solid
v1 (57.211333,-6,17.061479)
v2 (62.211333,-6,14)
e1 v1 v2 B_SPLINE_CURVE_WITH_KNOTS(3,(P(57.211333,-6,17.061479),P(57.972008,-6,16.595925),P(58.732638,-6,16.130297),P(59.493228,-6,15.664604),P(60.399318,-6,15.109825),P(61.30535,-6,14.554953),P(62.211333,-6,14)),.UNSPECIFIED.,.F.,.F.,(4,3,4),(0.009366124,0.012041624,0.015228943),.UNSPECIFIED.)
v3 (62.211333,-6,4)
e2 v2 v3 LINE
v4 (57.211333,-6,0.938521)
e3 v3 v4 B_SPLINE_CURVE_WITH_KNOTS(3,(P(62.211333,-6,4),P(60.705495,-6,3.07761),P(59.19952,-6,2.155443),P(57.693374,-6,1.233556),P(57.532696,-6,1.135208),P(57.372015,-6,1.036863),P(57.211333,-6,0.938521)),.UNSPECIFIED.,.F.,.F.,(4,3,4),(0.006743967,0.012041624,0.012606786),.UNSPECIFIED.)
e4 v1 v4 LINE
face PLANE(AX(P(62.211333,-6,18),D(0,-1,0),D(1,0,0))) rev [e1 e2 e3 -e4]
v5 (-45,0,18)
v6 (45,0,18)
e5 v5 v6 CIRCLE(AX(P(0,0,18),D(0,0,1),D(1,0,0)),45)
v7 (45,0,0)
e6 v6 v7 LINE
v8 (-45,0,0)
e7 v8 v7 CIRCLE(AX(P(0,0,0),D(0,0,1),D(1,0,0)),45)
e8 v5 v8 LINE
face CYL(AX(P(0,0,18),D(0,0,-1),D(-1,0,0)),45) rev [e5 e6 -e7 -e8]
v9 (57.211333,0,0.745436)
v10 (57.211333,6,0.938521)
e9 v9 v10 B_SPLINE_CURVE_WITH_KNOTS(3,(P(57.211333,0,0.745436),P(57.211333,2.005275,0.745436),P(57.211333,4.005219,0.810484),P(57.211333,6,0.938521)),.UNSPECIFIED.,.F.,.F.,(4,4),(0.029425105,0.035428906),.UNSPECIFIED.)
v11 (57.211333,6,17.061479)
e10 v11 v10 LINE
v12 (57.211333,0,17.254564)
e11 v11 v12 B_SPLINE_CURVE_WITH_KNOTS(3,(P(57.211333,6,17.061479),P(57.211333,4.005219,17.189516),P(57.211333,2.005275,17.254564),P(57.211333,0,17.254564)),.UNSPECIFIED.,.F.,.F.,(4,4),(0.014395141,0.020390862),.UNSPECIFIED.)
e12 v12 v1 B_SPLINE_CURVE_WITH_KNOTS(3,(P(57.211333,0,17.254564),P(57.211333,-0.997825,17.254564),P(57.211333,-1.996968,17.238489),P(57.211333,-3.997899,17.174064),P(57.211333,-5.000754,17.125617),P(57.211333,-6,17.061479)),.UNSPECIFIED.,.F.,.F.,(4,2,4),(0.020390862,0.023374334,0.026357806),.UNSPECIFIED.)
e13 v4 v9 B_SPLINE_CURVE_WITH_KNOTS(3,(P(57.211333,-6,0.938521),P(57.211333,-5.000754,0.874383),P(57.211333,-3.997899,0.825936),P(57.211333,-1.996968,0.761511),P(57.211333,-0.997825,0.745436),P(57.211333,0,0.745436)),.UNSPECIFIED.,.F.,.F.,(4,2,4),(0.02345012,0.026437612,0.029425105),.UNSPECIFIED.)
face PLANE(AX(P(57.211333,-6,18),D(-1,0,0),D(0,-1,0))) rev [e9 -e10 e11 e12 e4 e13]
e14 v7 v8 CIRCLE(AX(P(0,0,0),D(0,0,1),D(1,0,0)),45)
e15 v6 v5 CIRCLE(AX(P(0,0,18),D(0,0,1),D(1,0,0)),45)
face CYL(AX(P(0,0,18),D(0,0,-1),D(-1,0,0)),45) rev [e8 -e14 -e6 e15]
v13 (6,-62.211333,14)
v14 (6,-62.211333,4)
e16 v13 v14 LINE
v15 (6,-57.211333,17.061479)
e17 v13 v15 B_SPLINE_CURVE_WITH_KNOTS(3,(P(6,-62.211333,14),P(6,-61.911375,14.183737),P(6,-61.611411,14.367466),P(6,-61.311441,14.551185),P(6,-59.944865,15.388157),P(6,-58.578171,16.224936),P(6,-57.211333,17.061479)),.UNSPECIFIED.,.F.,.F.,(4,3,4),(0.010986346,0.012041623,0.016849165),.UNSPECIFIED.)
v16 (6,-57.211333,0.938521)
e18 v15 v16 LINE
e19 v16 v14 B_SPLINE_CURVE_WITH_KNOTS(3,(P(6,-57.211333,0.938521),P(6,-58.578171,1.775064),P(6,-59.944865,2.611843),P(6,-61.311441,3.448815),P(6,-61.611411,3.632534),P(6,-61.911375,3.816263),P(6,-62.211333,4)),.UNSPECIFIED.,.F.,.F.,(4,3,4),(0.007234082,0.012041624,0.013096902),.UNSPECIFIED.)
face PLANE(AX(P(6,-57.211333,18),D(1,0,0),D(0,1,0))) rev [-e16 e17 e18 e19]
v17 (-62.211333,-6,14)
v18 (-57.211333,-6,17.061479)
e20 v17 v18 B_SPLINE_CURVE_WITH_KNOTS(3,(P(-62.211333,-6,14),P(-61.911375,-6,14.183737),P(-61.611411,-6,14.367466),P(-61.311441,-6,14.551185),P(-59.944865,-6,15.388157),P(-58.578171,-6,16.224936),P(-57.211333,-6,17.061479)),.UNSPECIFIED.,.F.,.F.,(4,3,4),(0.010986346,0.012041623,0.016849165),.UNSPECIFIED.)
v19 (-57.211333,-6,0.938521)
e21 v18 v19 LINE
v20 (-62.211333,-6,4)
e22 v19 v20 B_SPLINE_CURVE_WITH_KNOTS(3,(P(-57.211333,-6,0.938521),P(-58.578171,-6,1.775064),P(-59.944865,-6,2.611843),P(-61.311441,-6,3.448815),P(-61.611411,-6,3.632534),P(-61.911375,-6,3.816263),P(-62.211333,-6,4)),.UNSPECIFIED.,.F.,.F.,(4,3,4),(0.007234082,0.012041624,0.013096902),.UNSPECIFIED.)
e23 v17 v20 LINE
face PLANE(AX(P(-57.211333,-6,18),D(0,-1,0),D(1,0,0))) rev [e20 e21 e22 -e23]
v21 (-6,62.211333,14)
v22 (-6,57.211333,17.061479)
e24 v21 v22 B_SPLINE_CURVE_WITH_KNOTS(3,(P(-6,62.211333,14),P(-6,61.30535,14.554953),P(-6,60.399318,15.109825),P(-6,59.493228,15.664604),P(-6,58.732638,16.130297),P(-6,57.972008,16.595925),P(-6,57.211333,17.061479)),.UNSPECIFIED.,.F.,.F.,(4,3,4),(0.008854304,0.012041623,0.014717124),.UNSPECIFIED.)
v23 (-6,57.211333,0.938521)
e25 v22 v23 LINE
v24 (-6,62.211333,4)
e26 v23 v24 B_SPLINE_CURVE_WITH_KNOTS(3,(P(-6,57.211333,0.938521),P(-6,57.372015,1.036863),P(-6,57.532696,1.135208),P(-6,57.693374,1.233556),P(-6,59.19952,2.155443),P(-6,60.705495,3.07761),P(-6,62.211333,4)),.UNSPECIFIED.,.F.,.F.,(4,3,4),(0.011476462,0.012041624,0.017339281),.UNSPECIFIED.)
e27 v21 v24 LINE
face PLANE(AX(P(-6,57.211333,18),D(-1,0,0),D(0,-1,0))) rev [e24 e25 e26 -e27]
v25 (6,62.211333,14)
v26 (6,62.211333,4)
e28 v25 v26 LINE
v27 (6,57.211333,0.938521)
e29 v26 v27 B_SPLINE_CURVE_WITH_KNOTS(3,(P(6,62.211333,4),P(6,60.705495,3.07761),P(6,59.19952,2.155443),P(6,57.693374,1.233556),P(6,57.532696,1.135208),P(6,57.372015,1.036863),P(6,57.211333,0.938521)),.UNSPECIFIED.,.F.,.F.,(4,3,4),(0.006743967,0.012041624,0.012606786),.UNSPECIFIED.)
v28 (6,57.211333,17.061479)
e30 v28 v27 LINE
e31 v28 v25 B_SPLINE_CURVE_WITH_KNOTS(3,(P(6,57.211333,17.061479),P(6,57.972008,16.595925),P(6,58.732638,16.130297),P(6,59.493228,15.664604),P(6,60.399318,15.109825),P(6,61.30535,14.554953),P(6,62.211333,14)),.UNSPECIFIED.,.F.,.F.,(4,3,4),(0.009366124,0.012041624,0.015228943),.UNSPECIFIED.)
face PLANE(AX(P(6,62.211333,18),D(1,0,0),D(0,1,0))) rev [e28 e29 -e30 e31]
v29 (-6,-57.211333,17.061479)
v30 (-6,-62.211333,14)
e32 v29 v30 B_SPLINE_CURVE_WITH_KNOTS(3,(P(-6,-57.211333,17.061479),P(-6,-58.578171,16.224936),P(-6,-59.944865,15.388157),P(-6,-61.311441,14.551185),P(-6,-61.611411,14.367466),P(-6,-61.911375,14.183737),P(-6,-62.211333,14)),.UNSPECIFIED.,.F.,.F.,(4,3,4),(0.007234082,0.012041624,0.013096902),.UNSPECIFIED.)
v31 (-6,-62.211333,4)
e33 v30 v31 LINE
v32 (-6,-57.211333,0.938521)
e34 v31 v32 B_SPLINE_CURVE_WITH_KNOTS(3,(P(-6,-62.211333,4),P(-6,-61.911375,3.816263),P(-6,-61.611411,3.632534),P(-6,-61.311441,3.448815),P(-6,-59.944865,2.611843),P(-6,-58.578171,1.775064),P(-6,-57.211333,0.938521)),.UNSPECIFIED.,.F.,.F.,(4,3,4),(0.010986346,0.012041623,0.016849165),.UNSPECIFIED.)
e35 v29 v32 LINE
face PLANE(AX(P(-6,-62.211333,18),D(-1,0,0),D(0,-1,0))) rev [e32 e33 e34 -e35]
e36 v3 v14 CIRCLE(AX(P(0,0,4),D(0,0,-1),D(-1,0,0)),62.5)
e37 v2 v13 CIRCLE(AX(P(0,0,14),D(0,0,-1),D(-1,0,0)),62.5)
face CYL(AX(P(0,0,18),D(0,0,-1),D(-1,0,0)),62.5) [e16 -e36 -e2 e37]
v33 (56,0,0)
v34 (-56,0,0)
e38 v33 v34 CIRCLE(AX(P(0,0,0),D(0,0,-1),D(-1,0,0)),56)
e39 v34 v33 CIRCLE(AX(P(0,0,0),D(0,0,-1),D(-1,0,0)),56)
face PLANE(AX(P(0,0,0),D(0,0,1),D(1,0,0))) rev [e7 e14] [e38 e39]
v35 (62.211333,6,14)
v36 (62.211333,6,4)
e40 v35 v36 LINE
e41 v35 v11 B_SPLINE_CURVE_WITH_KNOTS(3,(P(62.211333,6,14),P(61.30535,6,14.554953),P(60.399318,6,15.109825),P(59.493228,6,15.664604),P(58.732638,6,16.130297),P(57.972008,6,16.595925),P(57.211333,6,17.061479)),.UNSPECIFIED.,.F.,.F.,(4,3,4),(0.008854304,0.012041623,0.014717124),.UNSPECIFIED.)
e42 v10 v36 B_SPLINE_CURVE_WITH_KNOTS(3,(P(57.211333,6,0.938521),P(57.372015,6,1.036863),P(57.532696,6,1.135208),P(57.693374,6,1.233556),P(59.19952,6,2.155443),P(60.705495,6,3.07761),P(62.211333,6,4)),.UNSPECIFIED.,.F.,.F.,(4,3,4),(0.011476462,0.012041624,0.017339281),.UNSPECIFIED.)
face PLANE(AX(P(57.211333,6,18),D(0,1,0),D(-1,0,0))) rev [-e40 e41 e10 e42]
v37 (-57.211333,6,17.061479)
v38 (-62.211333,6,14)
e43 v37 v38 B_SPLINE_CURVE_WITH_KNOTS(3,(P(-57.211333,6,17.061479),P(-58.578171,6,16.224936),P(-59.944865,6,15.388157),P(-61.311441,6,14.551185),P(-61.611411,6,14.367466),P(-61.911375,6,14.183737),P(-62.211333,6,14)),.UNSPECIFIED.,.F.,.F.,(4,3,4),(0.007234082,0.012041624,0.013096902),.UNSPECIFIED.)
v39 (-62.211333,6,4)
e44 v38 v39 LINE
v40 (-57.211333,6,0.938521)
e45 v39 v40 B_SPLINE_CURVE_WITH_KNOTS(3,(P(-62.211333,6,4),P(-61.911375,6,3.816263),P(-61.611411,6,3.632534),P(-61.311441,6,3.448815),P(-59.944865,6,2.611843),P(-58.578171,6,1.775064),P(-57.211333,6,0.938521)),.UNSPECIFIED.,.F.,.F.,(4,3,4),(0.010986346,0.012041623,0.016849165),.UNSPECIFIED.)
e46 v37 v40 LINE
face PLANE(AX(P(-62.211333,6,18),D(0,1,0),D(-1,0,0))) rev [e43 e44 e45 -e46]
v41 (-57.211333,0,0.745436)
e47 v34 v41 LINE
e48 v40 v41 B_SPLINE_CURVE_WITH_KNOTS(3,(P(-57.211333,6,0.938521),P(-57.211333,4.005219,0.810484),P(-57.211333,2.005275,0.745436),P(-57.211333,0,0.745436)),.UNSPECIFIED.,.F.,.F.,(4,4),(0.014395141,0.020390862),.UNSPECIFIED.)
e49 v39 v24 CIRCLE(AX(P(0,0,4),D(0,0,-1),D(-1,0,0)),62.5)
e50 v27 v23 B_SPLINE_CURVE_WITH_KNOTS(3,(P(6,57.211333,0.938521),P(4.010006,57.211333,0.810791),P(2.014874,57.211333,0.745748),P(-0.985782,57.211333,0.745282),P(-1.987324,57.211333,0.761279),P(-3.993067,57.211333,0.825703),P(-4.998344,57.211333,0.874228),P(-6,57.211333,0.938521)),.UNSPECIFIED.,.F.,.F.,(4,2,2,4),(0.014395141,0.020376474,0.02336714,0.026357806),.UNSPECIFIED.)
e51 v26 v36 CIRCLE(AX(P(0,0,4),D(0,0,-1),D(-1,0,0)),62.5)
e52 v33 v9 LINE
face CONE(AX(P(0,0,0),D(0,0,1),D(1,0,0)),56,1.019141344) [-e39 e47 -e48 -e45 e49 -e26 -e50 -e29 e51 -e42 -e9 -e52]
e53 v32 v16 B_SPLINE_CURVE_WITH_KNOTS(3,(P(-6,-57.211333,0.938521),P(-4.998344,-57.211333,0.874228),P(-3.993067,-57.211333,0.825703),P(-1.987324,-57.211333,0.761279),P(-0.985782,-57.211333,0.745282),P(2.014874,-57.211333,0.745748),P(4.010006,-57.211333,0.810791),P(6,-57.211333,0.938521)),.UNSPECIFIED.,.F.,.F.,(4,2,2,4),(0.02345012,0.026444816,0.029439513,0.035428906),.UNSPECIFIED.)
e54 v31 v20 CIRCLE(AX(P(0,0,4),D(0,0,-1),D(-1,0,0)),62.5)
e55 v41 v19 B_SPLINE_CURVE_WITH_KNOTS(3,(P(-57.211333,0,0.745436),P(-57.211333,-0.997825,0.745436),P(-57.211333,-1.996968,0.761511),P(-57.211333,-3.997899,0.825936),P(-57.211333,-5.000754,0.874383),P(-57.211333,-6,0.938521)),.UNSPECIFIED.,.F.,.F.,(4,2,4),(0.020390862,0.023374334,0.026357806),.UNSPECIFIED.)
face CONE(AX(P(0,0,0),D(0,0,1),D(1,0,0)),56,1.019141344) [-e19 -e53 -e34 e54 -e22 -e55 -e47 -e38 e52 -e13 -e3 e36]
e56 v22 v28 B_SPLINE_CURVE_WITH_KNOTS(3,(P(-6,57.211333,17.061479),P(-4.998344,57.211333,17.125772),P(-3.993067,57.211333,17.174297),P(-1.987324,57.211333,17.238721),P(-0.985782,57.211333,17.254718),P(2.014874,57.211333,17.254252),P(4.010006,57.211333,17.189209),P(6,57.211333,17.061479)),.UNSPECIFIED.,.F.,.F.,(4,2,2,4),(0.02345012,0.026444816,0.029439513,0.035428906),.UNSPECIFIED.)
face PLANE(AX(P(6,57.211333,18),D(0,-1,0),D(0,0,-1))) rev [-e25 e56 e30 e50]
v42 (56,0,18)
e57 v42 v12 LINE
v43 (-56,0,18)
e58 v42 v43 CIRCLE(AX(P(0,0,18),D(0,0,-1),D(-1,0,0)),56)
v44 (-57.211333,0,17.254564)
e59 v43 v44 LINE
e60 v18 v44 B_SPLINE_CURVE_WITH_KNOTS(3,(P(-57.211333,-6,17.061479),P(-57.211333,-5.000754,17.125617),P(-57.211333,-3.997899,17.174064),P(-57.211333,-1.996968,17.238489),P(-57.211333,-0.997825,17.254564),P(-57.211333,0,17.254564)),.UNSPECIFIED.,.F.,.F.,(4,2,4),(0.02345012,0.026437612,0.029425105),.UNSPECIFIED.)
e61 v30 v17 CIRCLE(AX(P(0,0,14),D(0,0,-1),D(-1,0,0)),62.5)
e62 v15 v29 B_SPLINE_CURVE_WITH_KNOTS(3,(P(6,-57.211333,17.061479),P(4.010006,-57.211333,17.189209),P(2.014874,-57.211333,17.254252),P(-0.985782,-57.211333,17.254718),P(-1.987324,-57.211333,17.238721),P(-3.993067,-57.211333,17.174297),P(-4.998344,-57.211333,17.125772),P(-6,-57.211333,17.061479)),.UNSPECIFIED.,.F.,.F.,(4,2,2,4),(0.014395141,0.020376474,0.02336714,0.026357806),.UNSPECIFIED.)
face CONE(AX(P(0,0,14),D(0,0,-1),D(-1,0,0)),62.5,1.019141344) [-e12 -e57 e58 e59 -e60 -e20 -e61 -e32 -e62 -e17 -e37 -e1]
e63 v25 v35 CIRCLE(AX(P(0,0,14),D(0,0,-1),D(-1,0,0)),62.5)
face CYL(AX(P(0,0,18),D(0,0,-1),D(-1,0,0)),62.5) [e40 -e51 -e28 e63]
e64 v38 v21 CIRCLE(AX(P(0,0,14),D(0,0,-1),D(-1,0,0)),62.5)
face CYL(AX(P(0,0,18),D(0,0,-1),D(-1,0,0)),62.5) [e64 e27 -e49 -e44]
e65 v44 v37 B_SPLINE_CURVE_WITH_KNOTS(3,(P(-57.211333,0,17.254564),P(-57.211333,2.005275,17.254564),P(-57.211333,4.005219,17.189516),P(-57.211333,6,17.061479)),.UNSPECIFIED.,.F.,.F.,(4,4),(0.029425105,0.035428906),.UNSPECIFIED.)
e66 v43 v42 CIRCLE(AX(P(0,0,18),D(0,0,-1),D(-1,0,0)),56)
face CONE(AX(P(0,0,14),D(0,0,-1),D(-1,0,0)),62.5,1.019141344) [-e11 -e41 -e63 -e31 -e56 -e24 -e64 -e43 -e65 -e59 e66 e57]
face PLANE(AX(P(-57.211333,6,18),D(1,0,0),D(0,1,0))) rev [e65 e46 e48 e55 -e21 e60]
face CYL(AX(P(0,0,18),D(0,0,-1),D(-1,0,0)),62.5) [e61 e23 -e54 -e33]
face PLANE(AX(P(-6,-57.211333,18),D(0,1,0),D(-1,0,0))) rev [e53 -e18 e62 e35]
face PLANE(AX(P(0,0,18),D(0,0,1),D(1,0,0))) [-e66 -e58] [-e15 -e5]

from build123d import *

# Parameters (mm, degrees)
SKETCH_1_R          = 62.5
SKETCH_1_R_2        = 45
EXTRUDE_1_DEPTH     = 18
CUT_EXTRUDE_1_DEPTH = 18


with BuildPart() as part:
    # 草图1 → 凸台-拉伸1 (new body)
    with BuildSketch(Plane.XY):
        Circle(SKETCH_1_R)
        Circle(SKETCH_1_R_2, mode=Mode.SUBTRACT)
    extrude(amount=EXTRUDE_1_DEPTH)

    # 草图2 → 切除-旋转1 (revolve, cut)
    with BuildSketch(Plane(origin=(0, 0, 0), x_dir=(1, 0, 0), z_dir=(0, 1, 0)), mode=Mode.PRIVATE) as cut_revolve_1_sk:
        Polygon((62.5, -4), (62.5, 0), (56, 0), align=None)
        Polygon((62.5, -14), (62.5, -18), (56, -18), align=None)
    revolve(cut_revolve_1_sk.sketch.rotate(Axis((0, 0, -32.669833972), (0, 0, 1)), 180), axis=Axis((0, 0, -32.669833972), (0, 0, 1)), mode=Mode.SUBTRACT)

    # 草图3 → 切除-拉伸1 (cut)
    with BuildSketch(Plane(origin=(0, 0, 0), x_dir=(-1, 0, 0), z_dir=(0, 0, -1))):
        with BuildLine():
            Line((-6, 62.211333373), (-6, 57.211333373))
            Line((-6, 57.211333373), (6, 57.211333373))
            Line((6, 57.211333373), (6, 62.211333373))
            ThreePointArc((6, 62.211333373), (0, 62.5), (-6, 62.211333373))
        make_face()
        with BuildLine():
            Line((62.211333373, 6), (57.211333373, 6))
            Line((57.211333373, 6), (57.211333373, -6))
            Line((57.211333373, -6), (62.211333373, -6))
            ThreePointArc((62.211333373, -6), (62.5, 0), (62.211333373, 6))
        make_face()
        with BuildLine():
            Line((6, -62.211333373), (6, -57.211333373))
            Line((6, -57.211333373), (-6, -57.211333373))
            Line((-6, -57.211333373), (-6, -62.211333373))
            ThreePointArc((-6, -62.211333373), (0, -62.5), (6, -62.211333373))
        make_face()
        with BuildLine():
            Line((-62.211333373, -6), (-57.211333373, -6))
            Line((-57.211333373, -6), (-57.211333373, 6))
            Line((-57.211333373, 6), (-62.211333373, 6))
            ThreePointArc((-62.211333373, 6), (-62.5, 0), (-62.211333373, -6))
        make_face()
    extrude(amount=-CUT_EXTRUDE_1_DEPTH, mode=Mode.SUBTRACT)


solid = part.part
